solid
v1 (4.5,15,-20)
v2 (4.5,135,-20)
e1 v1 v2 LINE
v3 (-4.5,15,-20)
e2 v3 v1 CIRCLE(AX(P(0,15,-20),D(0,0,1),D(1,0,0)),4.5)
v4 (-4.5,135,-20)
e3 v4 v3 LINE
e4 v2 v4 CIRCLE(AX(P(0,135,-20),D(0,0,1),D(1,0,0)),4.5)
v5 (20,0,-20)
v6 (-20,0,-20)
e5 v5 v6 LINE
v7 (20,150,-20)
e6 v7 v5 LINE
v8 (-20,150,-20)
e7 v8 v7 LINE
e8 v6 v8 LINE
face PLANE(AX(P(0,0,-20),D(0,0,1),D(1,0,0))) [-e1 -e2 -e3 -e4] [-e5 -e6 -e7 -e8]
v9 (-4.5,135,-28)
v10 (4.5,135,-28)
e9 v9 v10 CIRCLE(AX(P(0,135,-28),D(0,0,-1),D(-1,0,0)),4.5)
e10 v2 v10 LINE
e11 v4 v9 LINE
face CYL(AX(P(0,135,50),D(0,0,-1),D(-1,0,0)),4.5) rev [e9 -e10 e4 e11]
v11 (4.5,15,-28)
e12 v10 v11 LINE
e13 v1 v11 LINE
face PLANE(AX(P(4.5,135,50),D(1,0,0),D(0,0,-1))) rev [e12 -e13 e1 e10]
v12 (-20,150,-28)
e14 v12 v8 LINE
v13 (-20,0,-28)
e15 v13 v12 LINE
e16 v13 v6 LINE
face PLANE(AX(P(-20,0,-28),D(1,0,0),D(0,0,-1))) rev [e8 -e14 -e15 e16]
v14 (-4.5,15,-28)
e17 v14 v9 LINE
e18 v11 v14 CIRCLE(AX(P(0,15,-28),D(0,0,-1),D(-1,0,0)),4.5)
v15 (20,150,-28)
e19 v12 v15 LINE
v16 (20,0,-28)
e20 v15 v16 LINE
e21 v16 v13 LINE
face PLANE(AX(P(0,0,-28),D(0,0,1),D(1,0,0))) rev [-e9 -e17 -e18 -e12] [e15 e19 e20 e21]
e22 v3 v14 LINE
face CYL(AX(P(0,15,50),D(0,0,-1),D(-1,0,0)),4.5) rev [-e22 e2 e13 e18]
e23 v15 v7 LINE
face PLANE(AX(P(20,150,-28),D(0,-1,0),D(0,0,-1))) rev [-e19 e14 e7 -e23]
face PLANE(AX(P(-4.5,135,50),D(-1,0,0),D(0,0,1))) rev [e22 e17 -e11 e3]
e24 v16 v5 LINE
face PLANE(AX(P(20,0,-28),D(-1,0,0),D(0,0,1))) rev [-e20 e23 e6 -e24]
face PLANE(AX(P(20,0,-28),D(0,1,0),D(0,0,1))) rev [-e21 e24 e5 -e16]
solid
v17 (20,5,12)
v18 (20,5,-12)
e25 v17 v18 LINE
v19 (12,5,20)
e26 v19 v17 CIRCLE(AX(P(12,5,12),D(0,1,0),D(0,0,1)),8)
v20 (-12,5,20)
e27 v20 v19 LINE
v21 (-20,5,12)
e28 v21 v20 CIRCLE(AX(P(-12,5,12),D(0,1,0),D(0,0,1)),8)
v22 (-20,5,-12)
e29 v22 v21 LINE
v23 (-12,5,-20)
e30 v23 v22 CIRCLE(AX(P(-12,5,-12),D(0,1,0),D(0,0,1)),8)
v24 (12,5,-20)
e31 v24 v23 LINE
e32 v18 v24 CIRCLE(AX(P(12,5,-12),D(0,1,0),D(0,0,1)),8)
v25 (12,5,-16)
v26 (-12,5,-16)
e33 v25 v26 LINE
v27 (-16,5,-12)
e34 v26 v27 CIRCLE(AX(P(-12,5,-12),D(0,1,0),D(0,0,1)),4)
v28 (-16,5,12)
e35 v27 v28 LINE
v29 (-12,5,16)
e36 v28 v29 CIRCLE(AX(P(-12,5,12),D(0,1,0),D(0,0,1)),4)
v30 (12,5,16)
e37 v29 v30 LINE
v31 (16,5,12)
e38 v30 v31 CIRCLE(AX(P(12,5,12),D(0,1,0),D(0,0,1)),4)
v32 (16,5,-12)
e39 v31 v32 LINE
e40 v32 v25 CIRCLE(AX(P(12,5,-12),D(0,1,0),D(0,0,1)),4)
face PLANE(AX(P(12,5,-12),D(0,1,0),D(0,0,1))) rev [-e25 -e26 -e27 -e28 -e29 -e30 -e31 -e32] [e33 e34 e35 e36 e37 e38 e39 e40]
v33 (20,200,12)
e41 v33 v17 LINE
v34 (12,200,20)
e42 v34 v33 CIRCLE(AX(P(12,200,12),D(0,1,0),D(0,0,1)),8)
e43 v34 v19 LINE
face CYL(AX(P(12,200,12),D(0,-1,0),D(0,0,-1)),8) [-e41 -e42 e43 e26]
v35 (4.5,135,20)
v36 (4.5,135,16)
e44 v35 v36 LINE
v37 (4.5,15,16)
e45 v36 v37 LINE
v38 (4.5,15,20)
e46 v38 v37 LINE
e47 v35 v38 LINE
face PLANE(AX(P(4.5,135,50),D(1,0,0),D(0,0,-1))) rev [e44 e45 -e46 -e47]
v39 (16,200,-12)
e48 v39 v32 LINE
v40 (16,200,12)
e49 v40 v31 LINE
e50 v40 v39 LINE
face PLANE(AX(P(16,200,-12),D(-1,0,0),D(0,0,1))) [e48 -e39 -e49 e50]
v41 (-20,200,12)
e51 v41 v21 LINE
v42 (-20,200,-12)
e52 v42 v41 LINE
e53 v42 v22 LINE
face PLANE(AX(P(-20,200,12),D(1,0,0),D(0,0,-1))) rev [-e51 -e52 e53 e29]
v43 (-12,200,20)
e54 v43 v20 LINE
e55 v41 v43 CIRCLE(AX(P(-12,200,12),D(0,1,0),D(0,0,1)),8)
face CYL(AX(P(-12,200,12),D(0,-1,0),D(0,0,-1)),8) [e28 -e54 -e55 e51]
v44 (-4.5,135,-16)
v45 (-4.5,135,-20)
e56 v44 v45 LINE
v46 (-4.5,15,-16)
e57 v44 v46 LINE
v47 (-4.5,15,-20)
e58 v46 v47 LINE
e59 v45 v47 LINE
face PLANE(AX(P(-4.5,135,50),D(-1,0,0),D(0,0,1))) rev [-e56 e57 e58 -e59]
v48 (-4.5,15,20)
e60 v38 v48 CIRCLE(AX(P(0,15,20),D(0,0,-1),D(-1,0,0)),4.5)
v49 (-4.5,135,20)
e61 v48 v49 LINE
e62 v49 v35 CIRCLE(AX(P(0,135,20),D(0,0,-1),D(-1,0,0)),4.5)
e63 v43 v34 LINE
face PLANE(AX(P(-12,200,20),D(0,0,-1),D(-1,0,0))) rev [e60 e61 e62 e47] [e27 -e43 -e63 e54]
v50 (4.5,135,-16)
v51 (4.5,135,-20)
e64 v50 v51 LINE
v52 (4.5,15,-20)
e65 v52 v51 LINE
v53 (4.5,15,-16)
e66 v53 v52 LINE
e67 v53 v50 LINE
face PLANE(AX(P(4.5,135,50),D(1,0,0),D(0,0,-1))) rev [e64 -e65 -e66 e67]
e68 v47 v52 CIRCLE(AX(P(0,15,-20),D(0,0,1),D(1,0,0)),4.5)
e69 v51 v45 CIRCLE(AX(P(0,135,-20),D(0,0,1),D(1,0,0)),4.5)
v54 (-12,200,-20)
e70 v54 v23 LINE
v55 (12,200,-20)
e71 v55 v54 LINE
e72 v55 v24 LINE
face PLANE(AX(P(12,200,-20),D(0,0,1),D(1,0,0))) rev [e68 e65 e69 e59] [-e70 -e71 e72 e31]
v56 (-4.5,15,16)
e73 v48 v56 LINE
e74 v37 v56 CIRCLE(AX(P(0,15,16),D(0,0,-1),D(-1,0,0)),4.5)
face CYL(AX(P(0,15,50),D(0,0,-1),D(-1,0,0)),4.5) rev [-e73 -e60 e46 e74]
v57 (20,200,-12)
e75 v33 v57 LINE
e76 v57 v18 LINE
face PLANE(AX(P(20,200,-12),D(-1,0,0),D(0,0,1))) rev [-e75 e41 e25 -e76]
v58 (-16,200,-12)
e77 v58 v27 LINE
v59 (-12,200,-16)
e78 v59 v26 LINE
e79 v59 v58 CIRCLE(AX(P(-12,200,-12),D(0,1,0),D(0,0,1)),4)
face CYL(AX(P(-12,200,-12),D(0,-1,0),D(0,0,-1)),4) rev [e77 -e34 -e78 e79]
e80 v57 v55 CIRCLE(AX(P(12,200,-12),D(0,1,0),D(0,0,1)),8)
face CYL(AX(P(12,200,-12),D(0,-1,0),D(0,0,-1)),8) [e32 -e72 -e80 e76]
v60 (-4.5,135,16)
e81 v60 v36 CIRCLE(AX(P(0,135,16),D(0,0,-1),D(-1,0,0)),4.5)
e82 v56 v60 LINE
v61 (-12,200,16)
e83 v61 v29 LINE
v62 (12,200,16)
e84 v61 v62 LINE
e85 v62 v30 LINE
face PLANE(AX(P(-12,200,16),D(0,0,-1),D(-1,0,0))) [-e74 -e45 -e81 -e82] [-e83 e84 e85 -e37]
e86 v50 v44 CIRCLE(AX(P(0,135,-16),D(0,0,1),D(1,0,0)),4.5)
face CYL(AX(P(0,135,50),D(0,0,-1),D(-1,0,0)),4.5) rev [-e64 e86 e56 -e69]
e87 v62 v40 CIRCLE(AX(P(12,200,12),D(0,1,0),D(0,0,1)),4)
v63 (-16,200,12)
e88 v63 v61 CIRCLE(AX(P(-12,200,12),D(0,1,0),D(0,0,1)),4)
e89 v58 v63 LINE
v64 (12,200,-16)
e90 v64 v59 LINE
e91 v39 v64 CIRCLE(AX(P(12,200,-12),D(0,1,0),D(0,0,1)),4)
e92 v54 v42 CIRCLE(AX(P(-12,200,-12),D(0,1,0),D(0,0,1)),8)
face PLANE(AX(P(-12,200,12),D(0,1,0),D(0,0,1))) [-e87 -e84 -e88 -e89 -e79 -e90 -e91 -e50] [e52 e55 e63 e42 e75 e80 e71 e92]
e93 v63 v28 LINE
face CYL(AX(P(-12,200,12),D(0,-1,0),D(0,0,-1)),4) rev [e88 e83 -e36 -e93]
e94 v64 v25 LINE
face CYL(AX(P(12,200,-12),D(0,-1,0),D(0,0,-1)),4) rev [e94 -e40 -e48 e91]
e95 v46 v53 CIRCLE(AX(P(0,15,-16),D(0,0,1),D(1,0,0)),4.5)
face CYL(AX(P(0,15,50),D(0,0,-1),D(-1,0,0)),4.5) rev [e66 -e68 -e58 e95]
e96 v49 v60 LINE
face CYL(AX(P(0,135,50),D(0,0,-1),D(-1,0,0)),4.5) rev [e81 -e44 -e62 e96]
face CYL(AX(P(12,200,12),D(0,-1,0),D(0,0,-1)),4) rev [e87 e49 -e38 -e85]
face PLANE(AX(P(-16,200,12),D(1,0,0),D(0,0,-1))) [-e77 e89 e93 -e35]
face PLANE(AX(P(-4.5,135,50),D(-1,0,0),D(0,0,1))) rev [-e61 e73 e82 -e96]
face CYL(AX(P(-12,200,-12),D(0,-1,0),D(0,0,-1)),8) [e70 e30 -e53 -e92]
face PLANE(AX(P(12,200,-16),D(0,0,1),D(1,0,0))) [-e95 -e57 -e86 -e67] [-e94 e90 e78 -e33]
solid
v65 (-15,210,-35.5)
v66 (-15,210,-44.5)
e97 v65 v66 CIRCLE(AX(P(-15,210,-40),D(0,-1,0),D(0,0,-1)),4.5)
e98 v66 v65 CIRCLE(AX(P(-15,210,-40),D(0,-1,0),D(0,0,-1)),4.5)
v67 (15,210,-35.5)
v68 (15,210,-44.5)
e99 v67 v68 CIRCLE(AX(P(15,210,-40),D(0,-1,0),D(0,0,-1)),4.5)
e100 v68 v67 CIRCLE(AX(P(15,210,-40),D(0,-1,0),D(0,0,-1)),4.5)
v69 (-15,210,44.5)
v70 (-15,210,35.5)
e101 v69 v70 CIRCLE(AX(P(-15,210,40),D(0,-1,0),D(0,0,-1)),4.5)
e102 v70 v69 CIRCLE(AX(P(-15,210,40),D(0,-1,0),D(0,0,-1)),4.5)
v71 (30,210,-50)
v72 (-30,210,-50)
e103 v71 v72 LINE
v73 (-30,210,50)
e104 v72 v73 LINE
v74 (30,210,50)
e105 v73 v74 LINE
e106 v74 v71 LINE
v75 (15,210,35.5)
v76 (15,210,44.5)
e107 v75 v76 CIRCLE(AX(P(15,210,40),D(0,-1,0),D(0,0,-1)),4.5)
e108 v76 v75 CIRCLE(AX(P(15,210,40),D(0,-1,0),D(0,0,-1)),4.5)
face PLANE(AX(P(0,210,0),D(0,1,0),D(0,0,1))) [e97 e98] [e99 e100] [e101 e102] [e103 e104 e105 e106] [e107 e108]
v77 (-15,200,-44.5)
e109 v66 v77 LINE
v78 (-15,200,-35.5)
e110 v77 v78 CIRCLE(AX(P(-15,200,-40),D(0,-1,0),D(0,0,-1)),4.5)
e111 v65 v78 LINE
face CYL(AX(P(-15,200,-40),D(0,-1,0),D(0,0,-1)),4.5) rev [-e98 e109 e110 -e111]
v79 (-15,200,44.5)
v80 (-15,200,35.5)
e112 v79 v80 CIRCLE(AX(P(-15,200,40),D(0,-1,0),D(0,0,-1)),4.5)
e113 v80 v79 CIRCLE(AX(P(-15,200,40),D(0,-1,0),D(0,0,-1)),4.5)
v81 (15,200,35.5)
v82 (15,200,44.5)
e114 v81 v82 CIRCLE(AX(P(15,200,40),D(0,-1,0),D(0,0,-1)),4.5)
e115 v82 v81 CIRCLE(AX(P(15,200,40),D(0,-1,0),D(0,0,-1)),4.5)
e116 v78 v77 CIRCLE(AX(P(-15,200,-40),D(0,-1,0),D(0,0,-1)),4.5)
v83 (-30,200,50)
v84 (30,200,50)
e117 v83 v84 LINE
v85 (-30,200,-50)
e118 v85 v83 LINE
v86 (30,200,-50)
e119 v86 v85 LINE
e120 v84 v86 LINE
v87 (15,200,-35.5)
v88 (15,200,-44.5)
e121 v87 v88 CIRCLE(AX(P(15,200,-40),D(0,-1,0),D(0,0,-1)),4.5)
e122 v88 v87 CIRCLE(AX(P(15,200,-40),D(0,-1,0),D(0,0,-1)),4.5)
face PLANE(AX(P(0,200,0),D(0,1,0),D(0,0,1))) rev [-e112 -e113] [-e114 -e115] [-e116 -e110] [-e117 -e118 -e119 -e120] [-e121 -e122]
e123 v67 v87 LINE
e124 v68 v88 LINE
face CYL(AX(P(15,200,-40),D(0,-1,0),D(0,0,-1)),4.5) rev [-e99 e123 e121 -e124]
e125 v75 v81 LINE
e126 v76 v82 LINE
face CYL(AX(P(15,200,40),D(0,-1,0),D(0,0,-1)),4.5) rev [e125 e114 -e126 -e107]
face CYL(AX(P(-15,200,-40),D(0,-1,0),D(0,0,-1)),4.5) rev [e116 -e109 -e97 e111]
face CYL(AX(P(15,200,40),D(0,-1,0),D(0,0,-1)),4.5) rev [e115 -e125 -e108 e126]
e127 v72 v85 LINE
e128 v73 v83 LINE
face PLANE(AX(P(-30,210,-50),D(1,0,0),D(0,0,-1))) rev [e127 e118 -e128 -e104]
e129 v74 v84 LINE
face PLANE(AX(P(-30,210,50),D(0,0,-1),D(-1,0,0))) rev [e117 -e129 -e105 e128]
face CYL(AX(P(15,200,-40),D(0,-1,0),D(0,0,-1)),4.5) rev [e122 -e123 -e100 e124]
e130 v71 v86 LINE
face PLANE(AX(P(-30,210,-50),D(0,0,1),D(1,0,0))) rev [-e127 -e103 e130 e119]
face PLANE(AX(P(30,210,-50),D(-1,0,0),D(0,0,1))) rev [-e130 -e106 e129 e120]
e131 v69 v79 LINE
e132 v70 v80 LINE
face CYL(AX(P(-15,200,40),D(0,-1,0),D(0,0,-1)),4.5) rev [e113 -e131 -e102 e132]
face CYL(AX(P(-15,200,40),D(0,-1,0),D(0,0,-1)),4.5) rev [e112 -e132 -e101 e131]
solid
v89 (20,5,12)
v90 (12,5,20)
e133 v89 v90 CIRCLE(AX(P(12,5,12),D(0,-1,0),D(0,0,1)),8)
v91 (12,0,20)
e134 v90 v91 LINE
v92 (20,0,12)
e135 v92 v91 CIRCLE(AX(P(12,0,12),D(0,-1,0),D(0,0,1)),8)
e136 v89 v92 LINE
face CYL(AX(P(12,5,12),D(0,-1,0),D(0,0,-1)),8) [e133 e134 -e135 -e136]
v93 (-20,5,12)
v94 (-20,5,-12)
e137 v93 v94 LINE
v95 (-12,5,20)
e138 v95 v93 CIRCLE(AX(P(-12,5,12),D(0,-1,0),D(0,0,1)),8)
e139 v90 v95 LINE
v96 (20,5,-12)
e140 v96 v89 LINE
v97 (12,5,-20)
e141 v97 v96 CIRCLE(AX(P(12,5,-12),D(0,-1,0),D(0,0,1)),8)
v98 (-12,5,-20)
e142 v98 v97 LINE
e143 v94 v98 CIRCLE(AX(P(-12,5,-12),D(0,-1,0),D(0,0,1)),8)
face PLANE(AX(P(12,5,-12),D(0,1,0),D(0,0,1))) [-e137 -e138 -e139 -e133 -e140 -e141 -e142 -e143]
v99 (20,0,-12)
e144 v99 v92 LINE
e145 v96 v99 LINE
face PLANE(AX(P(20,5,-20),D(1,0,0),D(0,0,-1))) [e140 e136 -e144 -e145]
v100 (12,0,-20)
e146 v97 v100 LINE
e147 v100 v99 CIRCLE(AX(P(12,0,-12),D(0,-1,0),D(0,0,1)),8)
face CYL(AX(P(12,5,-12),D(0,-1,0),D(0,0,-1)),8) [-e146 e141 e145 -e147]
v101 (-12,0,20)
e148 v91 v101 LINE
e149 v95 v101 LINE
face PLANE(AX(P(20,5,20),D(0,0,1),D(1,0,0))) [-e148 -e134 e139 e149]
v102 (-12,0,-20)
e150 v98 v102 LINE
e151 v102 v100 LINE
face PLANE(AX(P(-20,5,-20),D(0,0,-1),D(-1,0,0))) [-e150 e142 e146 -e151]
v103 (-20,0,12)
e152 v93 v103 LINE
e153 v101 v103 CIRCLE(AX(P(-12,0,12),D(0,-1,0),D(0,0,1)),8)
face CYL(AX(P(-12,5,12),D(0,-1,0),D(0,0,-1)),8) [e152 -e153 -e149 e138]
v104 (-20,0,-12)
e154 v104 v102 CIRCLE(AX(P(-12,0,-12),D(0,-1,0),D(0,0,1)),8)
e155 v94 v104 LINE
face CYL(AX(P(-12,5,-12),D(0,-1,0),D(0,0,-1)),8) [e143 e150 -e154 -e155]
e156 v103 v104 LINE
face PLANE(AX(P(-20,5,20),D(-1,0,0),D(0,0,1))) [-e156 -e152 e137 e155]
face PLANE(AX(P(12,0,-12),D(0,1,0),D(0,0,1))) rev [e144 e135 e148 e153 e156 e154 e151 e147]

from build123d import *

# Parameters (mm, degrees)
F_40_X_40_X_4_0_1_DEPTH        = 200
SKETCH_4_W                     = 60
SKETCH_4_H                     = 100
EXTRUDE_1_DEPTH                = 10
END_CAP_1_THICKNESS            = 5
SKETCH_6_W                     = 4.5
SKETCH_6_H                     = 10
HOLE_WIZARD_9_0_9_1_AT_2_COUNT = 2
HOLE_WIZARD_9_0_9_1_AT_2_PITCH = 30
HOLE_WIZARD_9_0_9_1_AT_3_COUNT = 2
HOLE_WIZARD_9_0_9_1_AT_3_PITCH = 80
HOLE_WIZARD_9_0_9_1_AT_4_COUNT = 2
HOLE_WIZARD_9_0_9_1_AT_4_PITCH = 85.440037453
SKETCH_8_W                     = 40
SKETCH_8_H                     = 150
EXTRUDE_2_DEPTH                = 8
CUT_EXTRUDE_1_DEPTH            = 227.017698422


with BuildPart() as part:
    # Sketch1 → 方管 40 X 40 X 4.0(1) (new body)
    with BuildSketch(Plane(origin=(0, 0, 0), x_dir=(-1, 0, 0), z_dir=(0, 1, 0))):
        with BuildLine():
            Line((-12, -20), (12, -20))
            ThreePointArc((12, -20), (17.656854249, -17.656854249), (20, -12))
            Line((20, -12), (20, 12))
            ThreePointArc((20, 12), (17.656854249, 17.656854249), (12, 20))
            Line((12, 20), (-12, 20))
            ThreePointArc((-12, 20), (-17.656854249, 17.656854249), (-20, 12))
            Line((-20, 12), (-20, -12))
            ThreePointArc((-20, -12), (-17.656854249, -17.656854249), (-12, -20))
        make_face()
        with BuildLine():
            Line((-12, -16), (12, -16))
            ThreePointArc((12, -16), (14.828427125, -14.828427125), (16, -12))
            Line((16, -12), (16, 12))
            ThreePointArc((16, 12), (14.828427125, 14.828427125), (12, 16))
            Line((12, 16), (-12, 16))
            ThreePointArc((-12, 16), (-14.828427125, 14.828427125), (-16, 12))
            Line((-16, 12), (-16, -12))
            ThreePointArc((-16, -12), (-14.828427125, -14.828427125), (-12, -16))
        make_face(mode=Mode.SUBTRACT)
    extrude(amount=F_40_X_40_X_4_0_1_DEPTH)


with BuildPart() as body_2:
    # 草图4 → 凸台-拉伸1 (new body)
    with BuildSketch(Plane(origin=(0, 200, 0), x_dir=(1, 0, 0), z_dir=(0, 1, 0))):
        Rectangle(SKETCH_4_W, SKETCH_4_H)
    extrude(amount=EXTRUDE_1_DEPTH)

    # 草图6 → Ø9.0 (9) 直径孔1 (revolve, cut)
    with BuildSketch(Plane(origin=(15, 200, -40), x_dir=(0, 0, -1), z_dir=(1, 0, 0))):
        with Locations((2.25, 5)):
            Rectangle(SKETCH_6_W, SKETCH_6_H)
    hole_wizard_9_0_9_1 = revolve(axis=Axis((15, 193.65, -40), (0, 1, 0)), mode=Mode.SUBTRACT)

    # Ø9.0 (9) 直径孔1 at 2: Ø9.0 (9) 直径孔1 ×2
    with Locations(*[(-i * HOLE_WIZARD_9_0_9_1_AT_2_PITCH, 0, 0) for i in range(1, HOLE_WIZARD_9_0_9_1_AT_2_COUNT)]):
        add(hole_wizard_9_0_9_1, mode=Mode.SUBTRACT)

    # Ø9.0 (9) 直径孔1 at 3: Ø9.0 (9) 直径孔1 ×2
    with Locations(*[(0, 0, i * HOLE_WIZARD_9_0_9_1_AT_3_PITCH) for i in range(1, HOLE_WIZARD_9_0_9_1_AT_3_COUNT)]):
        add(hole_wizard_9_0_9_1, mode=Mode.SUBTRACT)

    # Ø9.0 (9) 直径孔1 at 4: Ø9.0 (9) 直径孔1 ×2
    with Locations(*[Vector(-0.3511234415883917, 0, 0.9363291775690445) * (i * HOLE_WIZARD_9_0_9_1_AT_4_PITCH) for i in range(1, HOLE_WIZARD_9_0_9_1_AT_4_COUNT)]):
        add(hole_wizard_9_0_9_1, mode=Mode.SUBTRACT)


with BuildPart() as body_3:
    # End Cap 1: an end cap: a plate 5.0 thick on the member's open end, its outline the end's outer outline
    end_cap_1_end = part.part.faces().sort_by_distance((16, 0, -16))[0]
    add(extrude(Face(end_cap_1_end.outer_wire()), amount=END_CAP_1_THICKNESS, dir=(0, 1, 0)))


with BuildPart() as part_1:
    add(part.part)

    # End Cap 1 3
    split(bisect_by=Plane(origin=(0, 5, 0), x_dir=(-1, 0, 0), z_dir=(0, 1, 0)), keep=Keep.TOP)


with BuildPart() as body_4:
    # 草图8 → 凸台-拉伸2 (new body)
    with BuildSketch(Plane(origin=(0, 0, -20), x_dir=(-1, 0, 0), z_dir=(0, 0, -1))):
        with Locations((0, 75)):
            Rectangle(SKETCH_8_W, SKETCH_8_H)
    extrude(amount=EXTRUDE_2_DEPTH)


with BuildPart() as cut_extrude_1_tool:
    # 草图9 → 切除-拉伸1 (new, through all)
    with BuildSketch(Plane(origin=(0, 0, -28), x_dir=(-1, 0, 0), z_dir=(0, 0, -1))):
        with BuildLine():
            Line((4.5, 135), (4.5, 15))
            ThreePointArc((4.5, 15), (0, 10.5), (-4.5, 15))
            Line((-4.5, 15), (-4.5, 135))
            ThreePointArc((-4.5, 135), (0, 139.5), (4.5, 135))
        make_face()
    extrude(amount=-CUT_EXTRUDE_1_DEPTH)


with BuildPart() as part_2:
    add(part_1.part)

    # 切除-拉伸1: cut by cut_extrude_1_tool
    add(cut_extrude_1_tool.part, mode=Mode.SUBTRACT)


with BuildPart() as body_4_1:
    add(body_4.part)

    # 切除-拉伸1: cut by cut_extrude_1_tool
    add(cut_extrude_1_tool.part, mode=Mode.SUBTRACT)


solid = Compound([body_2.part, body_3.part, part_2.part, body_4_1.part])
